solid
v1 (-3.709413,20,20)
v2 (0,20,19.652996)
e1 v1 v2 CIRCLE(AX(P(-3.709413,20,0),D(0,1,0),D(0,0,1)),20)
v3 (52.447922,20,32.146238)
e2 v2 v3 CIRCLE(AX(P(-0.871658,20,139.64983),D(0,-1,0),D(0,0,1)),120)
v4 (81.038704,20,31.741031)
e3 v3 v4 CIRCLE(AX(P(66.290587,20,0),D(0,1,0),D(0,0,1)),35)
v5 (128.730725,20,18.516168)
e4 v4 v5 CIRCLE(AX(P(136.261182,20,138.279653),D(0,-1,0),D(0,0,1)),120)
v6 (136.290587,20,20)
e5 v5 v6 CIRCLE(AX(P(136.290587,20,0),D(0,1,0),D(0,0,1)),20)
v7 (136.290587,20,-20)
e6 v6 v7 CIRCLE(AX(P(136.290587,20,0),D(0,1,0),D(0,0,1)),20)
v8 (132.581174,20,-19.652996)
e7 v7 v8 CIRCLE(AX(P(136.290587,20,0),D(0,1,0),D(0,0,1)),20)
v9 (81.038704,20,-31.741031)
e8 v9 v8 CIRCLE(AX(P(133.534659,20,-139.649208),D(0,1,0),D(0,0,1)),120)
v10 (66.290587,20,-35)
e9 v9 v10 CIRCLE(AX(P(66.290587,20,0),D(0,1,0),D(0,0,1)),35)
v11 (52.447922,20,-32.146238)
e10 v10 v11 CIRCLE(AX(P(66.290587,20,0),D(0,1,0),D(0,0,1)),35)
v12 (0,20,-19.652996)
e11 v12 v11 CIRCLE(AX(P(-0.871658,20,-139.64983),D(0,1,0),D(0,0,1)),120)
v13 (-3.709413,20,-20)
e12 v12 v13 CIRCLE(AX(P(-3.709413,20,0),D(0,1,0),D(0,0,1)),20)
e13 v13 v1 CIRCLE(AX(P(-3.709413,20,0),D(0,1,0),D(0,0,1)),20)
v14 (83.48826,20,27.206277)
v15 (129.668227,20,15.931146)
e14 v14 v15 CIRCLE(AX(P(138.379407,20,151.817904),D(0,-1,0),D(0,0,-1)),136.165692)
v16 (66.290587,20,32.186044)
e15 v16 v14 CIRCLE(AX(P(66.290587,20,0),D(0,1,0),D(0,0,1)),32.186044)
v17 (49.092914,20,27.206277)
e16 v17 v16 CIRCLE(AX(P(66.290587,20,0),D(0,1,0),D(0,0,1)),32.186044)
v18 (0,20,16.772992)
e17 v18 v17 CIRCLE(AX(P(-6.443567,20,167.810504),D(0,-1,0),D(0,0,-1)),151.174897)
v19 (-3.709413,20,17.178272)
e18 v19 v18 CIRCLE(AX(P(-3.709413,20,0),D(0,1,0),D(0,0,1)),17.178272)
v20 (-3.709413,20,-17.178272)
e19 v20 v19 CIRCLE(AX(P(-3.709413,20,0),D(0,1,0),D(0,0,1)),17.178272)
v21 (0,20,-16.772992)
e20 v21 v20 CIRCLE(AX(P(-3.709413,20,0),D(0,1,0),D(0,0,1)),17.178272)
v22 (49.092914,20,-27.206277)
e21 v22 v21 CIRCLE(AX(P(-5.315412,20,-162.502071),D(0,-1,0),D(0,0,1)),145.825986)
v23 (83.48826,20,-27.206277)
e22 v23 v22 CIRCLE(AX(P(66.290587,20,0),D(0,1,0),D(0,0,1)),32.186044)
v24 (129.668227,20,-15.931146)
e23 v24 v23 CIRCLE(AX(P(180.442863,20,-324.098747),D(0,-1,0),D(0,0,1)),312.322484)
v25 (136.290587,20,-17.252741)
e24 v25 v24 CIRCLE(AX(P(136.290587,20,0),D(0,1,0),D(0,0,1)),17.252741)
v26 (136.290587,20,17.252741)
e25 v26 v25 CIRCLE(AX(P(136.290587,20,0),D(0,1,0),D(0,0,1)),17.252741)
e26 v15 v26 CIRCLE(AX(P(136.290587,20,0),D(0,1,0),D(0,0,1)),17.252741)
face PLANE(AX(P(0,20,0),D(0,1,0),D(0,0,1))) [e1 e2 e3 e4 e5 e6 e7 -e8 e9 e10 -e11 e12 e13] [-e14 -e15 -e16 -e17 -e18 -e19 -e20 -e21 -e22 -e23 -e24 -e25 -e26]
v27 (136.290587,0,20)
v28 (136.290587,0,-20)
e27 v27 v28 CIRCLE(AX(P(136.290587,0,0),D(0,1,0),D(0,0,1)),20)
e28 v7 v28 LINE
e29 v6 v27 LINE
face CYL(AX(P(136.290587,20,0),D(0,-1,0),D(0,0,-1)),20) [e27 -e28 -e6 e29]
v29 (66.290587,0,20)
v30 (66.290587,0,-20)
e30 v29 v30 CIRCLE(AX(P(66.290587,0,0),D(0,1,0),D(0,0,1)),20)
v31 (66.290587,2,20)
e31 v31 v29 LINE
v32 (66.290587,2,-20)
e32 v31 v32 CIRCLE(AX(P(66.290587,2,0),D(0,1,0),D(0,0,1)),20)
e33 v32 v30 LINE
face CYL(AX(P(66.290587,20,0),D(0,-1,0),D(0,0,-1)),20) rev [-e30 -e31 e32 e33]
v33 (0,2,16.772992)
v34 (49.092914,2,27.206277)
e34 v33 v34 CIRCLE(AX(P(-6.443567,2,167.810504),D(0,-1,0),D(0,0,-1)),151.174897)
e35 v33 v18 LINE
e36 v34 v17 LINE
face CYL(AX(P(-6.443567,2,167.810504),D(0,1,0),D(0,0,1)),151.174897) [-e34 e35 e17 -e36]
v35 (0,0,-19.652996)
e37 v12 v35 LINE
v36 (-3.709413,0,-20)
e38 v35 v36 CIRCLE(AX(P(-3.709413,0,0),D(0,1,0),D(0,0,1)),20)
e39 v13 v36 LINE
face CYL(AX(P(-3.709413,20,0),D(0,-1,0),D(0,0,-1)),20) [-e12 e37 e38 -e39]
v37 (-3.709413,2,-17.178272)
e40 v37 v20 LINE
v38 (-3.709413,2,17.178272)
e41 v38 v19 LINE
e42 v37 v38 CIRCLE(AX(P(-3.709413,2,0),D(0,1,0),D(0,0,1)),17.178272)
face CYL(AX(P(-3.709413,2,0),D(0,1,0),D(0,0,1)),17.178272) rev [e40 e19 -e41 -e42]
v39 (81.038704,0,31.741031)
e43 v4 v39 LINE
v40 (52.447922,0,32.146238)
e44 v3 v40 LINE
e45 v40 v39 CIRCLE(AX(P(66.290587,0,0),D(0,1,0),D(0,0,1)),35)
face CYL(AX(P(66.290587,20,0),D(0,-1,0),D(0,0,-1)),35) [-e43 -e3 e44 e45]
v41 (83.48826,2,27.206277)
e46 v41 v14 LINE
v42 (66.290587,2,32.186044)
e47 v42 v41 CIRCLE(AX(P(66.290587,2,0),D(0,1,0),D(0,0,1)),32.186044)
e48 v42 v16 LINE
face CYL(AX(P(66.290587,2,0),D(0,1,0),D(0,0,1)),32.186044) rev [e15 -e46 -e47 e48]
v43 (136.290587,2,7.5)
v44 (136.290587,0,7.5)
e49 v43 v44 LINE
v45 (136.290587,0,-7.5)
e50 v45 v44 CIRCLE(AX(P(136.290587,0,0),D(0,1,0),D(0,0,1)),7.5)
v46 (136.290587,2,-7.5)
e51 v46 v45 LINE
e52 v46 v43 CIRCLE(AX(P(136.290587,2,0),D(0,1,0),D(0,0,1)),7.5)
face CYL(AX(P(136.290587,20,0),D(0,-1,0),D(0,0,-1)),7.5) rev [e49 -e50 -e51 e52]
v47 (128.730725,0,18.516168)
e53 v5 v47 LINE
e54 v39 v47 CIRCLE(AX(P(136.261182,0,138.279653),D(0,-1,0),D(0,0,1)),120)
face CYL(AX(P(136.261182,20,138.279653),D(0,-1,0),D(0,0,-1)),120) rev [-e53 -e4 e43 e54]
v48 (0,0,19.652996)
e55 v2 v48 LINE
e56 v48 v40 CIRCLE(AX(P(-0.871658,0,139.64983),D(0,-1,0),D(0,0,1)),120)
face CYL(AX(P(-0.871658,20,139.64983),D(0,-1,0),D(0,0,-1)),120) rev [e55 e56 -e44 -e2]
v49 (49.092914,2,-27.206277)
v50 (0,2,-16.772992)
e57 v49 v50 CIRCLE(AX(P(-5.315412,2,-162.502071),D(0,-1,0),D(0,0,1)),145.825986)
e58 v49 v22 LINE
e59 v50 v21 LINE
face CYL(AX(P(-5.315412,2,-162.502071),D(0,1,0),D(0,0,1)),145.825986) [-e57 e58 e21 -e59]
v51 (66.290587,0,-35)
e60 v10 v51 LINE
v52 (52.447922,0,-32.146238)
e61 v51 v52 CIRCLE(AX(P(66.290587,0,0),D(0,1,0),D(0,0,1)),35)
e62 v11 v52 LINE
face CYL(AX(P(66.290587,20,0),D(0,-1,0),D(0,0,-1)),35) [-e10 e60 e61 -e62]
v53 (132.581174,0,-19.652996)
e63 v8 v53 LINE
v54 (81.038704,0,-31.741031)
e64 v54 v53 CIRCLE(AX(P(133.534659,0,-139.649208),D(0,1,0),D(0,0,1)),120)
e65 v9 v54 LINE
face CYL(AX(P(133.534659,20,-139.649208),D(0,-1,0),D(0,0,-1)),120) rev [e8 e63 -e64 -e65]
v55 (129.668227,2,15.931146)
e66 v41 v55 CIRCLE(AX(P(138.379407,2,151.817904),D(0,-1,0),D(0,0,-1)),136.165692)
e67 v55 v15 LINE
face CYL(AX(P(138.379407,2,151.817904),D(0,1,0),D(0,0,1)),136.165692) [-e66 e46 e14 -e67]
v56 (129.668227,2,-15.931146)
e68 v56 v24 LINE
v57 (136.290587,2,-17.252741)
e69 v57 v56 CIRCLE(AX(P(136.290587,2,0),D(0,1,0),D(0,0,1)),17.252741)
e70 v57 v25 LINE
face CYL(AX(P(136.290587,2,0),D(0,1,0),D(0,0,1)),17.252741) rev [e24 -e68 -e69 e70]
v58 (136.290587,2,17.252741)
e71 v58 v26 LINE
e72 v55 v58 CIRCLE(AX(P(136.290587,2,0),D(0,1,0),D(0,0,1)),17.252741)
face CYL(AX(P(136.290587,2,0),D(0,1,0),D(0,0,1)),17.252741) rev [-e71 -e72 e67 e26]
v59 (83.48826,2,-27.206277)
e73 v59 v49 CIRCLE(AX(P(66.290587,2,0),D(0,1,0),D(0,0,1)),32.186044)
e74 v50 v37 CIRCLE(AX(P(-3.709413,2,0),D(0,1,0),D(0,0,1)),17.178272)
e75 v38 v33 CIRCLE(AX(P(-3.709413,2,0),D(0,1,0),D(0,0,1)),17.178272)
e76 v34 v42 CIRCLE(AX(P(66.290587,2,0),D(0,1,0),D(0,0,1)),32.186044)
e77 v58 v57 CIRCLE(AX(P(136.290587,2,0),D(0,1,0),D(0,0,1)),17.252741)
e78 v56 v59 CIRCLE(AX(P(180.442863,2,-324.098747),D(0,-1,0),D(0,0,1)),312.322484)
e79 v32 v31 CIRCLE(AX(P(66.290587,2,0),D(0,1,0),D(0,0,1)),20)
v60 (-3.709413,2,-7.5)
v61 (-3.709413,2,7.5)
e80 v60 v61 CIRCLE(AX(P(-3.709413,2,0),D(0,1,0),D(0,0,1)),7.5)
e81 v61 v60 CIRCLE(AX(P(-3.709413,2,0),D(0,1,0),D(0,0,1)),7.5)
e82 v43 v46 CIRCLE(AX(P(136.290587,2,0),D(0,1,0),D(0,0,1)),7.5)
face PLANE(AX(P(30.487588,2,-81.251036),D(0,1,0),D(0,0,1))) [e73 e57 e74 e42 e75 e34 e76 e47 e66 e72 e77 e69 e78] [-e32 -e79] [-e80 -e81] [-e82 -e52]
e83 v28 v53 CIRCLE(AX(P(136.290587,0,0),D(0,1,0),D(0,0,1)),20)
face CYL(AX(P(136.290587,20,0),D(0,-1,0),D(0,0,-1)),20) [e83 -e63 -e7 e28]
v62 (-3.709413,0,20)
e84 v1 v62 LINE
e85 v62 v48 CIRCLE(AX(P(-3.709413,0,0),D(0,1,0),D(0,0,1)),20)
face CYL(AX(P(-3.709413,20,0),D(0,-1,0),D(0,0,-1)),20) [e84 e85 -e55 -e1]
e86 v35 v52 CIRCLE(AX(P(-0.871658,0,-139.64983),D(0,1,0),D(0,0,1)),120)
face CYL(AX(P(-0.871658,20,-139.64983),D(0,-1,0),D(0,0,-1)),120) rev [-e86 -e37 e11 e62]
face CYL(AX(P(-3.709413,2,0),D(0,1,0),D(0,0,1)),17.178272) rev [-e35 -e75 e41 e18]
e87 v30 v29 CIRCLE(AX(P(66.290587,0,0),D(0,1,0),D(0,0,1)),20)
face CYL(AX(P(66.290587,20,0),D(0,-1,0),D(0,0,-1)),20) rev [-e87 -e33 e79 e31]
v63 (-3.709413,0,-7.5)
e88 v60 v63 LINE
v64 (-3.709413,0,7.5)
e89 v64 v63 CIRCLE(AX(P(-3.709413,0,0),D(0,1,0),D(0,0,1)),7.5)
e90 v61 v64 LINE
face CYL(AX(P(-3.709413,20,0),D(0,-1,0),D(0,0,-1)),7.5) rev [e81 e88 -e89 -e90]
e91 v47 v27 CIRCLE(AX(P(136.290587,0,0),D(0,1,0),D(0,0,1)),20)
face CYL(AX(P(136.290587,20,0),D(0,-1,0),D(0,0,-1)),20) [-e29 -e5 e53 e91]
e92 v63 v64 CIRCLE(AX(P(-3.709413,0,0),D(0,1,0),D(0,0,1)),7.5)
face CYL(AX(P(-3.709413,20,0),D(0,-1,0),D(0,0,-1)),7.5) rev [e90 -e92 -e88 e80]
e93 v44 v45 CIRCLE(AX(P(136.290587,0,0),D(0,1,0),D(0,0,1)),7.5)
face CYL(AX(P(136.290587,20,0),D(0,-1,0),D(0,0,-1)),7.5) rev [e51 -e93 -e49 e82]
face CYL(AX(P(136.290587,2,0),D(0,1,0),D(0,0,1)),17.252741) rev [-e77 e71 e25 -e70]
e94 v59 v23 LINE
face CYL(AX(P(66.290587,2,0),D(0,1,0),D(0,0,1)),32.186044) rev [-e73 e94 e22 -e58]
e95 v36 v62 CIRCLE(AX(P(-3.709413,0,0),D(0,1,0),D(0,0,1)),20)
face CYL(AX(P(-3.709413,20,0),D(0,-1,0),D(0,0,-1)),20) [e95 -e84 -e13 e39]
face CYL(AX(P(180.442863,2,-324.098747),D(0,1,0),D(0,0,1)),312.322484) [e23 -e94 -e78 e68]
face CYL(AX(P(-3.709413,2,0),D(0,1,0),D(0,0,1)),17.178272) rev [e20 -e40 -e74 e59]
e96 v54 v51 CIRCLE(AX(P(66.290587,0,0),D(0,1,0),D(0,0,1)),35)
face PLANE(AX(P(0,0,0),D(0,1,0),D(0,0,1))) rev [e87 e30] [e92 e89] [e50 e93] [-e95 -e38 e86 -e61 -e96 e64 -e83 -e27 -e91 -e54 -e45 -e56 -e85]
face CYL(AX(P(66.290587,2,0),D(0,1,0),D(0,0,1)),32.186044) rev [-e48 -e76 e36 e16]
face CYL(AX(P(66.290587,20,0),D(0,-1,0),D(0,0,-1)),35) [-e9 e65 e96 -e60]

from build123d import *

# Parameters (mm, degrees)
PLATE_OUTLINE_AND_HOLES_SKETCH_R   = 7.5
PLATE_OUTLINE_AND_HOLES_SKETCH_R_2 = 20
PLATE_BODY_20MM_DEPTH              = 20
POCKET_18MM_DEEP_DEPTH             = 18


with BuildPart() as part:
    # Plate Outline and Holes Sketch → Plate Body 20mm (new body)
    with BuildSketch(Plane(origin=(0, 0, 0), x_dir=(1, 0, 0), z_dir=(0, 1, 0))):
        with BuildLine():
            ThreePointArc((0, -19.652996117), (25.514601751, -22.586747832), (49.820562895, -30.88265372))
            ThreePointArc((49.820562895, -30.88265372), (51.138080036, -31.506466617), (52.447922151, -32.146238124))
            ThreePointArc((52.447922151, -32.146238124), (66.786580153, -34.996485409), (81.03870417, -31.741030931))
            ThreePointArc((81.03870417, -31.741030931), (82.081542873, -31.206935864), (83.12954659, -30.683048174))
            ThreePointArc((83.12954659, -30.683048174), (105.326078872, -22.335617103), (128.730725009, -18.516168186))
            ThreePointArc((128.730725009, -18.516168186), (156.18959255, -2.007382475), (132.581174315, 19.652996117))
            ThreePointArc((132.581174315, 19.652996117), (106.605286262, 22.709869626), (81.908714055, 31.322102615))
            ThreePointArc((81.908714055, 31.322102615), (81.473287731, 31.530691668), (81.03870417, 31.741030931))
            ThreePointArc((81.03870417, 31.741030931), (66.786580153, 34.996485409), (52.447922151, 32.146238124))
            ThreePointArc((52.447922151, 32.146238124), (51.138080036, 31.506466617), (49.820562895, 30.88265372))
            ThreePointArc((49.820562895, 30.88265372), (25.514601751, 22.586747832), (0, 19.652996117))
            ThreePointArc((0, 19.652996117), (-23.709412843, 0), (0, -19.652996117))
        make_face()
        with Locations(Location((-3.709412843, 0, 0), (0, 0, 270))):
            Circle(PLATE_OUTLINE_AND_HOLES_SKETCH_R, mode=Mode.SUBTRACT)
        with Locations(Location((66.290587157, 0, 0), (0, 0, 270))):
            Circle(PLATE_OUTLINE_AND_HOLES_SKETCH_R_2, mode=Mode.SUBTRACT)
        with Locations(Location((136.290587157, 0, 0), (0, 0, 270))):
            Circle(PLATE_OUTLINE_AND_HOLES_SKETCH_R, mode=Mode.SUBTRACT)
    extrude(amount=PLATE_BODY_20MM_DEPTH)

    # Pocket Outline Sketch → Pocket 18mm Deep (cut)
    with BuildSketch(Plane(origin=(0, 20, 0), x_dir=(1, 0, 0), z_dir=(0, 1, 0))):
        with BuildLine():
            ThreePointArc((0, 16.772992409), (-20.887684525, 0), (0, -16.772992409))
            ThreePointArc((0, -16.772992409), (24.982456418, -19.938077439), (49.092914173, -27.206276583))
            ThreePointArc((49.092914173, -27.206276583), (66.290587157, -32.186044206), (83.488260142, -27.206276583))
            ThreePointArc((83.488260142, -27.206276583), (106.082407894, -19.537899767), (129.668226583, -15.931146045))
            ThreePointArc((129.668226583, -15.931146045), (153.543328212, 0), (129.668226583, 15.931146045))
            ThreePointArc((129.668226583, 15.931146045), (106.363417967, 20.688843047), (83.488260142, 27.206276583))
            ThreePointArc((83.488260142, 27.206276583), (66.290587157, 32.186044206), (49.092914173, 27.206276583))
            ThreePointArc((49.092914173, 27.206276583), (24.998686698, 19.861707266), (0, 16.772992409))
        make_face()
    extrude(amount=-POCKET_18MM_DEEP_DEPTH, mode=Mode.SUBTRACT)


solid = part.part
